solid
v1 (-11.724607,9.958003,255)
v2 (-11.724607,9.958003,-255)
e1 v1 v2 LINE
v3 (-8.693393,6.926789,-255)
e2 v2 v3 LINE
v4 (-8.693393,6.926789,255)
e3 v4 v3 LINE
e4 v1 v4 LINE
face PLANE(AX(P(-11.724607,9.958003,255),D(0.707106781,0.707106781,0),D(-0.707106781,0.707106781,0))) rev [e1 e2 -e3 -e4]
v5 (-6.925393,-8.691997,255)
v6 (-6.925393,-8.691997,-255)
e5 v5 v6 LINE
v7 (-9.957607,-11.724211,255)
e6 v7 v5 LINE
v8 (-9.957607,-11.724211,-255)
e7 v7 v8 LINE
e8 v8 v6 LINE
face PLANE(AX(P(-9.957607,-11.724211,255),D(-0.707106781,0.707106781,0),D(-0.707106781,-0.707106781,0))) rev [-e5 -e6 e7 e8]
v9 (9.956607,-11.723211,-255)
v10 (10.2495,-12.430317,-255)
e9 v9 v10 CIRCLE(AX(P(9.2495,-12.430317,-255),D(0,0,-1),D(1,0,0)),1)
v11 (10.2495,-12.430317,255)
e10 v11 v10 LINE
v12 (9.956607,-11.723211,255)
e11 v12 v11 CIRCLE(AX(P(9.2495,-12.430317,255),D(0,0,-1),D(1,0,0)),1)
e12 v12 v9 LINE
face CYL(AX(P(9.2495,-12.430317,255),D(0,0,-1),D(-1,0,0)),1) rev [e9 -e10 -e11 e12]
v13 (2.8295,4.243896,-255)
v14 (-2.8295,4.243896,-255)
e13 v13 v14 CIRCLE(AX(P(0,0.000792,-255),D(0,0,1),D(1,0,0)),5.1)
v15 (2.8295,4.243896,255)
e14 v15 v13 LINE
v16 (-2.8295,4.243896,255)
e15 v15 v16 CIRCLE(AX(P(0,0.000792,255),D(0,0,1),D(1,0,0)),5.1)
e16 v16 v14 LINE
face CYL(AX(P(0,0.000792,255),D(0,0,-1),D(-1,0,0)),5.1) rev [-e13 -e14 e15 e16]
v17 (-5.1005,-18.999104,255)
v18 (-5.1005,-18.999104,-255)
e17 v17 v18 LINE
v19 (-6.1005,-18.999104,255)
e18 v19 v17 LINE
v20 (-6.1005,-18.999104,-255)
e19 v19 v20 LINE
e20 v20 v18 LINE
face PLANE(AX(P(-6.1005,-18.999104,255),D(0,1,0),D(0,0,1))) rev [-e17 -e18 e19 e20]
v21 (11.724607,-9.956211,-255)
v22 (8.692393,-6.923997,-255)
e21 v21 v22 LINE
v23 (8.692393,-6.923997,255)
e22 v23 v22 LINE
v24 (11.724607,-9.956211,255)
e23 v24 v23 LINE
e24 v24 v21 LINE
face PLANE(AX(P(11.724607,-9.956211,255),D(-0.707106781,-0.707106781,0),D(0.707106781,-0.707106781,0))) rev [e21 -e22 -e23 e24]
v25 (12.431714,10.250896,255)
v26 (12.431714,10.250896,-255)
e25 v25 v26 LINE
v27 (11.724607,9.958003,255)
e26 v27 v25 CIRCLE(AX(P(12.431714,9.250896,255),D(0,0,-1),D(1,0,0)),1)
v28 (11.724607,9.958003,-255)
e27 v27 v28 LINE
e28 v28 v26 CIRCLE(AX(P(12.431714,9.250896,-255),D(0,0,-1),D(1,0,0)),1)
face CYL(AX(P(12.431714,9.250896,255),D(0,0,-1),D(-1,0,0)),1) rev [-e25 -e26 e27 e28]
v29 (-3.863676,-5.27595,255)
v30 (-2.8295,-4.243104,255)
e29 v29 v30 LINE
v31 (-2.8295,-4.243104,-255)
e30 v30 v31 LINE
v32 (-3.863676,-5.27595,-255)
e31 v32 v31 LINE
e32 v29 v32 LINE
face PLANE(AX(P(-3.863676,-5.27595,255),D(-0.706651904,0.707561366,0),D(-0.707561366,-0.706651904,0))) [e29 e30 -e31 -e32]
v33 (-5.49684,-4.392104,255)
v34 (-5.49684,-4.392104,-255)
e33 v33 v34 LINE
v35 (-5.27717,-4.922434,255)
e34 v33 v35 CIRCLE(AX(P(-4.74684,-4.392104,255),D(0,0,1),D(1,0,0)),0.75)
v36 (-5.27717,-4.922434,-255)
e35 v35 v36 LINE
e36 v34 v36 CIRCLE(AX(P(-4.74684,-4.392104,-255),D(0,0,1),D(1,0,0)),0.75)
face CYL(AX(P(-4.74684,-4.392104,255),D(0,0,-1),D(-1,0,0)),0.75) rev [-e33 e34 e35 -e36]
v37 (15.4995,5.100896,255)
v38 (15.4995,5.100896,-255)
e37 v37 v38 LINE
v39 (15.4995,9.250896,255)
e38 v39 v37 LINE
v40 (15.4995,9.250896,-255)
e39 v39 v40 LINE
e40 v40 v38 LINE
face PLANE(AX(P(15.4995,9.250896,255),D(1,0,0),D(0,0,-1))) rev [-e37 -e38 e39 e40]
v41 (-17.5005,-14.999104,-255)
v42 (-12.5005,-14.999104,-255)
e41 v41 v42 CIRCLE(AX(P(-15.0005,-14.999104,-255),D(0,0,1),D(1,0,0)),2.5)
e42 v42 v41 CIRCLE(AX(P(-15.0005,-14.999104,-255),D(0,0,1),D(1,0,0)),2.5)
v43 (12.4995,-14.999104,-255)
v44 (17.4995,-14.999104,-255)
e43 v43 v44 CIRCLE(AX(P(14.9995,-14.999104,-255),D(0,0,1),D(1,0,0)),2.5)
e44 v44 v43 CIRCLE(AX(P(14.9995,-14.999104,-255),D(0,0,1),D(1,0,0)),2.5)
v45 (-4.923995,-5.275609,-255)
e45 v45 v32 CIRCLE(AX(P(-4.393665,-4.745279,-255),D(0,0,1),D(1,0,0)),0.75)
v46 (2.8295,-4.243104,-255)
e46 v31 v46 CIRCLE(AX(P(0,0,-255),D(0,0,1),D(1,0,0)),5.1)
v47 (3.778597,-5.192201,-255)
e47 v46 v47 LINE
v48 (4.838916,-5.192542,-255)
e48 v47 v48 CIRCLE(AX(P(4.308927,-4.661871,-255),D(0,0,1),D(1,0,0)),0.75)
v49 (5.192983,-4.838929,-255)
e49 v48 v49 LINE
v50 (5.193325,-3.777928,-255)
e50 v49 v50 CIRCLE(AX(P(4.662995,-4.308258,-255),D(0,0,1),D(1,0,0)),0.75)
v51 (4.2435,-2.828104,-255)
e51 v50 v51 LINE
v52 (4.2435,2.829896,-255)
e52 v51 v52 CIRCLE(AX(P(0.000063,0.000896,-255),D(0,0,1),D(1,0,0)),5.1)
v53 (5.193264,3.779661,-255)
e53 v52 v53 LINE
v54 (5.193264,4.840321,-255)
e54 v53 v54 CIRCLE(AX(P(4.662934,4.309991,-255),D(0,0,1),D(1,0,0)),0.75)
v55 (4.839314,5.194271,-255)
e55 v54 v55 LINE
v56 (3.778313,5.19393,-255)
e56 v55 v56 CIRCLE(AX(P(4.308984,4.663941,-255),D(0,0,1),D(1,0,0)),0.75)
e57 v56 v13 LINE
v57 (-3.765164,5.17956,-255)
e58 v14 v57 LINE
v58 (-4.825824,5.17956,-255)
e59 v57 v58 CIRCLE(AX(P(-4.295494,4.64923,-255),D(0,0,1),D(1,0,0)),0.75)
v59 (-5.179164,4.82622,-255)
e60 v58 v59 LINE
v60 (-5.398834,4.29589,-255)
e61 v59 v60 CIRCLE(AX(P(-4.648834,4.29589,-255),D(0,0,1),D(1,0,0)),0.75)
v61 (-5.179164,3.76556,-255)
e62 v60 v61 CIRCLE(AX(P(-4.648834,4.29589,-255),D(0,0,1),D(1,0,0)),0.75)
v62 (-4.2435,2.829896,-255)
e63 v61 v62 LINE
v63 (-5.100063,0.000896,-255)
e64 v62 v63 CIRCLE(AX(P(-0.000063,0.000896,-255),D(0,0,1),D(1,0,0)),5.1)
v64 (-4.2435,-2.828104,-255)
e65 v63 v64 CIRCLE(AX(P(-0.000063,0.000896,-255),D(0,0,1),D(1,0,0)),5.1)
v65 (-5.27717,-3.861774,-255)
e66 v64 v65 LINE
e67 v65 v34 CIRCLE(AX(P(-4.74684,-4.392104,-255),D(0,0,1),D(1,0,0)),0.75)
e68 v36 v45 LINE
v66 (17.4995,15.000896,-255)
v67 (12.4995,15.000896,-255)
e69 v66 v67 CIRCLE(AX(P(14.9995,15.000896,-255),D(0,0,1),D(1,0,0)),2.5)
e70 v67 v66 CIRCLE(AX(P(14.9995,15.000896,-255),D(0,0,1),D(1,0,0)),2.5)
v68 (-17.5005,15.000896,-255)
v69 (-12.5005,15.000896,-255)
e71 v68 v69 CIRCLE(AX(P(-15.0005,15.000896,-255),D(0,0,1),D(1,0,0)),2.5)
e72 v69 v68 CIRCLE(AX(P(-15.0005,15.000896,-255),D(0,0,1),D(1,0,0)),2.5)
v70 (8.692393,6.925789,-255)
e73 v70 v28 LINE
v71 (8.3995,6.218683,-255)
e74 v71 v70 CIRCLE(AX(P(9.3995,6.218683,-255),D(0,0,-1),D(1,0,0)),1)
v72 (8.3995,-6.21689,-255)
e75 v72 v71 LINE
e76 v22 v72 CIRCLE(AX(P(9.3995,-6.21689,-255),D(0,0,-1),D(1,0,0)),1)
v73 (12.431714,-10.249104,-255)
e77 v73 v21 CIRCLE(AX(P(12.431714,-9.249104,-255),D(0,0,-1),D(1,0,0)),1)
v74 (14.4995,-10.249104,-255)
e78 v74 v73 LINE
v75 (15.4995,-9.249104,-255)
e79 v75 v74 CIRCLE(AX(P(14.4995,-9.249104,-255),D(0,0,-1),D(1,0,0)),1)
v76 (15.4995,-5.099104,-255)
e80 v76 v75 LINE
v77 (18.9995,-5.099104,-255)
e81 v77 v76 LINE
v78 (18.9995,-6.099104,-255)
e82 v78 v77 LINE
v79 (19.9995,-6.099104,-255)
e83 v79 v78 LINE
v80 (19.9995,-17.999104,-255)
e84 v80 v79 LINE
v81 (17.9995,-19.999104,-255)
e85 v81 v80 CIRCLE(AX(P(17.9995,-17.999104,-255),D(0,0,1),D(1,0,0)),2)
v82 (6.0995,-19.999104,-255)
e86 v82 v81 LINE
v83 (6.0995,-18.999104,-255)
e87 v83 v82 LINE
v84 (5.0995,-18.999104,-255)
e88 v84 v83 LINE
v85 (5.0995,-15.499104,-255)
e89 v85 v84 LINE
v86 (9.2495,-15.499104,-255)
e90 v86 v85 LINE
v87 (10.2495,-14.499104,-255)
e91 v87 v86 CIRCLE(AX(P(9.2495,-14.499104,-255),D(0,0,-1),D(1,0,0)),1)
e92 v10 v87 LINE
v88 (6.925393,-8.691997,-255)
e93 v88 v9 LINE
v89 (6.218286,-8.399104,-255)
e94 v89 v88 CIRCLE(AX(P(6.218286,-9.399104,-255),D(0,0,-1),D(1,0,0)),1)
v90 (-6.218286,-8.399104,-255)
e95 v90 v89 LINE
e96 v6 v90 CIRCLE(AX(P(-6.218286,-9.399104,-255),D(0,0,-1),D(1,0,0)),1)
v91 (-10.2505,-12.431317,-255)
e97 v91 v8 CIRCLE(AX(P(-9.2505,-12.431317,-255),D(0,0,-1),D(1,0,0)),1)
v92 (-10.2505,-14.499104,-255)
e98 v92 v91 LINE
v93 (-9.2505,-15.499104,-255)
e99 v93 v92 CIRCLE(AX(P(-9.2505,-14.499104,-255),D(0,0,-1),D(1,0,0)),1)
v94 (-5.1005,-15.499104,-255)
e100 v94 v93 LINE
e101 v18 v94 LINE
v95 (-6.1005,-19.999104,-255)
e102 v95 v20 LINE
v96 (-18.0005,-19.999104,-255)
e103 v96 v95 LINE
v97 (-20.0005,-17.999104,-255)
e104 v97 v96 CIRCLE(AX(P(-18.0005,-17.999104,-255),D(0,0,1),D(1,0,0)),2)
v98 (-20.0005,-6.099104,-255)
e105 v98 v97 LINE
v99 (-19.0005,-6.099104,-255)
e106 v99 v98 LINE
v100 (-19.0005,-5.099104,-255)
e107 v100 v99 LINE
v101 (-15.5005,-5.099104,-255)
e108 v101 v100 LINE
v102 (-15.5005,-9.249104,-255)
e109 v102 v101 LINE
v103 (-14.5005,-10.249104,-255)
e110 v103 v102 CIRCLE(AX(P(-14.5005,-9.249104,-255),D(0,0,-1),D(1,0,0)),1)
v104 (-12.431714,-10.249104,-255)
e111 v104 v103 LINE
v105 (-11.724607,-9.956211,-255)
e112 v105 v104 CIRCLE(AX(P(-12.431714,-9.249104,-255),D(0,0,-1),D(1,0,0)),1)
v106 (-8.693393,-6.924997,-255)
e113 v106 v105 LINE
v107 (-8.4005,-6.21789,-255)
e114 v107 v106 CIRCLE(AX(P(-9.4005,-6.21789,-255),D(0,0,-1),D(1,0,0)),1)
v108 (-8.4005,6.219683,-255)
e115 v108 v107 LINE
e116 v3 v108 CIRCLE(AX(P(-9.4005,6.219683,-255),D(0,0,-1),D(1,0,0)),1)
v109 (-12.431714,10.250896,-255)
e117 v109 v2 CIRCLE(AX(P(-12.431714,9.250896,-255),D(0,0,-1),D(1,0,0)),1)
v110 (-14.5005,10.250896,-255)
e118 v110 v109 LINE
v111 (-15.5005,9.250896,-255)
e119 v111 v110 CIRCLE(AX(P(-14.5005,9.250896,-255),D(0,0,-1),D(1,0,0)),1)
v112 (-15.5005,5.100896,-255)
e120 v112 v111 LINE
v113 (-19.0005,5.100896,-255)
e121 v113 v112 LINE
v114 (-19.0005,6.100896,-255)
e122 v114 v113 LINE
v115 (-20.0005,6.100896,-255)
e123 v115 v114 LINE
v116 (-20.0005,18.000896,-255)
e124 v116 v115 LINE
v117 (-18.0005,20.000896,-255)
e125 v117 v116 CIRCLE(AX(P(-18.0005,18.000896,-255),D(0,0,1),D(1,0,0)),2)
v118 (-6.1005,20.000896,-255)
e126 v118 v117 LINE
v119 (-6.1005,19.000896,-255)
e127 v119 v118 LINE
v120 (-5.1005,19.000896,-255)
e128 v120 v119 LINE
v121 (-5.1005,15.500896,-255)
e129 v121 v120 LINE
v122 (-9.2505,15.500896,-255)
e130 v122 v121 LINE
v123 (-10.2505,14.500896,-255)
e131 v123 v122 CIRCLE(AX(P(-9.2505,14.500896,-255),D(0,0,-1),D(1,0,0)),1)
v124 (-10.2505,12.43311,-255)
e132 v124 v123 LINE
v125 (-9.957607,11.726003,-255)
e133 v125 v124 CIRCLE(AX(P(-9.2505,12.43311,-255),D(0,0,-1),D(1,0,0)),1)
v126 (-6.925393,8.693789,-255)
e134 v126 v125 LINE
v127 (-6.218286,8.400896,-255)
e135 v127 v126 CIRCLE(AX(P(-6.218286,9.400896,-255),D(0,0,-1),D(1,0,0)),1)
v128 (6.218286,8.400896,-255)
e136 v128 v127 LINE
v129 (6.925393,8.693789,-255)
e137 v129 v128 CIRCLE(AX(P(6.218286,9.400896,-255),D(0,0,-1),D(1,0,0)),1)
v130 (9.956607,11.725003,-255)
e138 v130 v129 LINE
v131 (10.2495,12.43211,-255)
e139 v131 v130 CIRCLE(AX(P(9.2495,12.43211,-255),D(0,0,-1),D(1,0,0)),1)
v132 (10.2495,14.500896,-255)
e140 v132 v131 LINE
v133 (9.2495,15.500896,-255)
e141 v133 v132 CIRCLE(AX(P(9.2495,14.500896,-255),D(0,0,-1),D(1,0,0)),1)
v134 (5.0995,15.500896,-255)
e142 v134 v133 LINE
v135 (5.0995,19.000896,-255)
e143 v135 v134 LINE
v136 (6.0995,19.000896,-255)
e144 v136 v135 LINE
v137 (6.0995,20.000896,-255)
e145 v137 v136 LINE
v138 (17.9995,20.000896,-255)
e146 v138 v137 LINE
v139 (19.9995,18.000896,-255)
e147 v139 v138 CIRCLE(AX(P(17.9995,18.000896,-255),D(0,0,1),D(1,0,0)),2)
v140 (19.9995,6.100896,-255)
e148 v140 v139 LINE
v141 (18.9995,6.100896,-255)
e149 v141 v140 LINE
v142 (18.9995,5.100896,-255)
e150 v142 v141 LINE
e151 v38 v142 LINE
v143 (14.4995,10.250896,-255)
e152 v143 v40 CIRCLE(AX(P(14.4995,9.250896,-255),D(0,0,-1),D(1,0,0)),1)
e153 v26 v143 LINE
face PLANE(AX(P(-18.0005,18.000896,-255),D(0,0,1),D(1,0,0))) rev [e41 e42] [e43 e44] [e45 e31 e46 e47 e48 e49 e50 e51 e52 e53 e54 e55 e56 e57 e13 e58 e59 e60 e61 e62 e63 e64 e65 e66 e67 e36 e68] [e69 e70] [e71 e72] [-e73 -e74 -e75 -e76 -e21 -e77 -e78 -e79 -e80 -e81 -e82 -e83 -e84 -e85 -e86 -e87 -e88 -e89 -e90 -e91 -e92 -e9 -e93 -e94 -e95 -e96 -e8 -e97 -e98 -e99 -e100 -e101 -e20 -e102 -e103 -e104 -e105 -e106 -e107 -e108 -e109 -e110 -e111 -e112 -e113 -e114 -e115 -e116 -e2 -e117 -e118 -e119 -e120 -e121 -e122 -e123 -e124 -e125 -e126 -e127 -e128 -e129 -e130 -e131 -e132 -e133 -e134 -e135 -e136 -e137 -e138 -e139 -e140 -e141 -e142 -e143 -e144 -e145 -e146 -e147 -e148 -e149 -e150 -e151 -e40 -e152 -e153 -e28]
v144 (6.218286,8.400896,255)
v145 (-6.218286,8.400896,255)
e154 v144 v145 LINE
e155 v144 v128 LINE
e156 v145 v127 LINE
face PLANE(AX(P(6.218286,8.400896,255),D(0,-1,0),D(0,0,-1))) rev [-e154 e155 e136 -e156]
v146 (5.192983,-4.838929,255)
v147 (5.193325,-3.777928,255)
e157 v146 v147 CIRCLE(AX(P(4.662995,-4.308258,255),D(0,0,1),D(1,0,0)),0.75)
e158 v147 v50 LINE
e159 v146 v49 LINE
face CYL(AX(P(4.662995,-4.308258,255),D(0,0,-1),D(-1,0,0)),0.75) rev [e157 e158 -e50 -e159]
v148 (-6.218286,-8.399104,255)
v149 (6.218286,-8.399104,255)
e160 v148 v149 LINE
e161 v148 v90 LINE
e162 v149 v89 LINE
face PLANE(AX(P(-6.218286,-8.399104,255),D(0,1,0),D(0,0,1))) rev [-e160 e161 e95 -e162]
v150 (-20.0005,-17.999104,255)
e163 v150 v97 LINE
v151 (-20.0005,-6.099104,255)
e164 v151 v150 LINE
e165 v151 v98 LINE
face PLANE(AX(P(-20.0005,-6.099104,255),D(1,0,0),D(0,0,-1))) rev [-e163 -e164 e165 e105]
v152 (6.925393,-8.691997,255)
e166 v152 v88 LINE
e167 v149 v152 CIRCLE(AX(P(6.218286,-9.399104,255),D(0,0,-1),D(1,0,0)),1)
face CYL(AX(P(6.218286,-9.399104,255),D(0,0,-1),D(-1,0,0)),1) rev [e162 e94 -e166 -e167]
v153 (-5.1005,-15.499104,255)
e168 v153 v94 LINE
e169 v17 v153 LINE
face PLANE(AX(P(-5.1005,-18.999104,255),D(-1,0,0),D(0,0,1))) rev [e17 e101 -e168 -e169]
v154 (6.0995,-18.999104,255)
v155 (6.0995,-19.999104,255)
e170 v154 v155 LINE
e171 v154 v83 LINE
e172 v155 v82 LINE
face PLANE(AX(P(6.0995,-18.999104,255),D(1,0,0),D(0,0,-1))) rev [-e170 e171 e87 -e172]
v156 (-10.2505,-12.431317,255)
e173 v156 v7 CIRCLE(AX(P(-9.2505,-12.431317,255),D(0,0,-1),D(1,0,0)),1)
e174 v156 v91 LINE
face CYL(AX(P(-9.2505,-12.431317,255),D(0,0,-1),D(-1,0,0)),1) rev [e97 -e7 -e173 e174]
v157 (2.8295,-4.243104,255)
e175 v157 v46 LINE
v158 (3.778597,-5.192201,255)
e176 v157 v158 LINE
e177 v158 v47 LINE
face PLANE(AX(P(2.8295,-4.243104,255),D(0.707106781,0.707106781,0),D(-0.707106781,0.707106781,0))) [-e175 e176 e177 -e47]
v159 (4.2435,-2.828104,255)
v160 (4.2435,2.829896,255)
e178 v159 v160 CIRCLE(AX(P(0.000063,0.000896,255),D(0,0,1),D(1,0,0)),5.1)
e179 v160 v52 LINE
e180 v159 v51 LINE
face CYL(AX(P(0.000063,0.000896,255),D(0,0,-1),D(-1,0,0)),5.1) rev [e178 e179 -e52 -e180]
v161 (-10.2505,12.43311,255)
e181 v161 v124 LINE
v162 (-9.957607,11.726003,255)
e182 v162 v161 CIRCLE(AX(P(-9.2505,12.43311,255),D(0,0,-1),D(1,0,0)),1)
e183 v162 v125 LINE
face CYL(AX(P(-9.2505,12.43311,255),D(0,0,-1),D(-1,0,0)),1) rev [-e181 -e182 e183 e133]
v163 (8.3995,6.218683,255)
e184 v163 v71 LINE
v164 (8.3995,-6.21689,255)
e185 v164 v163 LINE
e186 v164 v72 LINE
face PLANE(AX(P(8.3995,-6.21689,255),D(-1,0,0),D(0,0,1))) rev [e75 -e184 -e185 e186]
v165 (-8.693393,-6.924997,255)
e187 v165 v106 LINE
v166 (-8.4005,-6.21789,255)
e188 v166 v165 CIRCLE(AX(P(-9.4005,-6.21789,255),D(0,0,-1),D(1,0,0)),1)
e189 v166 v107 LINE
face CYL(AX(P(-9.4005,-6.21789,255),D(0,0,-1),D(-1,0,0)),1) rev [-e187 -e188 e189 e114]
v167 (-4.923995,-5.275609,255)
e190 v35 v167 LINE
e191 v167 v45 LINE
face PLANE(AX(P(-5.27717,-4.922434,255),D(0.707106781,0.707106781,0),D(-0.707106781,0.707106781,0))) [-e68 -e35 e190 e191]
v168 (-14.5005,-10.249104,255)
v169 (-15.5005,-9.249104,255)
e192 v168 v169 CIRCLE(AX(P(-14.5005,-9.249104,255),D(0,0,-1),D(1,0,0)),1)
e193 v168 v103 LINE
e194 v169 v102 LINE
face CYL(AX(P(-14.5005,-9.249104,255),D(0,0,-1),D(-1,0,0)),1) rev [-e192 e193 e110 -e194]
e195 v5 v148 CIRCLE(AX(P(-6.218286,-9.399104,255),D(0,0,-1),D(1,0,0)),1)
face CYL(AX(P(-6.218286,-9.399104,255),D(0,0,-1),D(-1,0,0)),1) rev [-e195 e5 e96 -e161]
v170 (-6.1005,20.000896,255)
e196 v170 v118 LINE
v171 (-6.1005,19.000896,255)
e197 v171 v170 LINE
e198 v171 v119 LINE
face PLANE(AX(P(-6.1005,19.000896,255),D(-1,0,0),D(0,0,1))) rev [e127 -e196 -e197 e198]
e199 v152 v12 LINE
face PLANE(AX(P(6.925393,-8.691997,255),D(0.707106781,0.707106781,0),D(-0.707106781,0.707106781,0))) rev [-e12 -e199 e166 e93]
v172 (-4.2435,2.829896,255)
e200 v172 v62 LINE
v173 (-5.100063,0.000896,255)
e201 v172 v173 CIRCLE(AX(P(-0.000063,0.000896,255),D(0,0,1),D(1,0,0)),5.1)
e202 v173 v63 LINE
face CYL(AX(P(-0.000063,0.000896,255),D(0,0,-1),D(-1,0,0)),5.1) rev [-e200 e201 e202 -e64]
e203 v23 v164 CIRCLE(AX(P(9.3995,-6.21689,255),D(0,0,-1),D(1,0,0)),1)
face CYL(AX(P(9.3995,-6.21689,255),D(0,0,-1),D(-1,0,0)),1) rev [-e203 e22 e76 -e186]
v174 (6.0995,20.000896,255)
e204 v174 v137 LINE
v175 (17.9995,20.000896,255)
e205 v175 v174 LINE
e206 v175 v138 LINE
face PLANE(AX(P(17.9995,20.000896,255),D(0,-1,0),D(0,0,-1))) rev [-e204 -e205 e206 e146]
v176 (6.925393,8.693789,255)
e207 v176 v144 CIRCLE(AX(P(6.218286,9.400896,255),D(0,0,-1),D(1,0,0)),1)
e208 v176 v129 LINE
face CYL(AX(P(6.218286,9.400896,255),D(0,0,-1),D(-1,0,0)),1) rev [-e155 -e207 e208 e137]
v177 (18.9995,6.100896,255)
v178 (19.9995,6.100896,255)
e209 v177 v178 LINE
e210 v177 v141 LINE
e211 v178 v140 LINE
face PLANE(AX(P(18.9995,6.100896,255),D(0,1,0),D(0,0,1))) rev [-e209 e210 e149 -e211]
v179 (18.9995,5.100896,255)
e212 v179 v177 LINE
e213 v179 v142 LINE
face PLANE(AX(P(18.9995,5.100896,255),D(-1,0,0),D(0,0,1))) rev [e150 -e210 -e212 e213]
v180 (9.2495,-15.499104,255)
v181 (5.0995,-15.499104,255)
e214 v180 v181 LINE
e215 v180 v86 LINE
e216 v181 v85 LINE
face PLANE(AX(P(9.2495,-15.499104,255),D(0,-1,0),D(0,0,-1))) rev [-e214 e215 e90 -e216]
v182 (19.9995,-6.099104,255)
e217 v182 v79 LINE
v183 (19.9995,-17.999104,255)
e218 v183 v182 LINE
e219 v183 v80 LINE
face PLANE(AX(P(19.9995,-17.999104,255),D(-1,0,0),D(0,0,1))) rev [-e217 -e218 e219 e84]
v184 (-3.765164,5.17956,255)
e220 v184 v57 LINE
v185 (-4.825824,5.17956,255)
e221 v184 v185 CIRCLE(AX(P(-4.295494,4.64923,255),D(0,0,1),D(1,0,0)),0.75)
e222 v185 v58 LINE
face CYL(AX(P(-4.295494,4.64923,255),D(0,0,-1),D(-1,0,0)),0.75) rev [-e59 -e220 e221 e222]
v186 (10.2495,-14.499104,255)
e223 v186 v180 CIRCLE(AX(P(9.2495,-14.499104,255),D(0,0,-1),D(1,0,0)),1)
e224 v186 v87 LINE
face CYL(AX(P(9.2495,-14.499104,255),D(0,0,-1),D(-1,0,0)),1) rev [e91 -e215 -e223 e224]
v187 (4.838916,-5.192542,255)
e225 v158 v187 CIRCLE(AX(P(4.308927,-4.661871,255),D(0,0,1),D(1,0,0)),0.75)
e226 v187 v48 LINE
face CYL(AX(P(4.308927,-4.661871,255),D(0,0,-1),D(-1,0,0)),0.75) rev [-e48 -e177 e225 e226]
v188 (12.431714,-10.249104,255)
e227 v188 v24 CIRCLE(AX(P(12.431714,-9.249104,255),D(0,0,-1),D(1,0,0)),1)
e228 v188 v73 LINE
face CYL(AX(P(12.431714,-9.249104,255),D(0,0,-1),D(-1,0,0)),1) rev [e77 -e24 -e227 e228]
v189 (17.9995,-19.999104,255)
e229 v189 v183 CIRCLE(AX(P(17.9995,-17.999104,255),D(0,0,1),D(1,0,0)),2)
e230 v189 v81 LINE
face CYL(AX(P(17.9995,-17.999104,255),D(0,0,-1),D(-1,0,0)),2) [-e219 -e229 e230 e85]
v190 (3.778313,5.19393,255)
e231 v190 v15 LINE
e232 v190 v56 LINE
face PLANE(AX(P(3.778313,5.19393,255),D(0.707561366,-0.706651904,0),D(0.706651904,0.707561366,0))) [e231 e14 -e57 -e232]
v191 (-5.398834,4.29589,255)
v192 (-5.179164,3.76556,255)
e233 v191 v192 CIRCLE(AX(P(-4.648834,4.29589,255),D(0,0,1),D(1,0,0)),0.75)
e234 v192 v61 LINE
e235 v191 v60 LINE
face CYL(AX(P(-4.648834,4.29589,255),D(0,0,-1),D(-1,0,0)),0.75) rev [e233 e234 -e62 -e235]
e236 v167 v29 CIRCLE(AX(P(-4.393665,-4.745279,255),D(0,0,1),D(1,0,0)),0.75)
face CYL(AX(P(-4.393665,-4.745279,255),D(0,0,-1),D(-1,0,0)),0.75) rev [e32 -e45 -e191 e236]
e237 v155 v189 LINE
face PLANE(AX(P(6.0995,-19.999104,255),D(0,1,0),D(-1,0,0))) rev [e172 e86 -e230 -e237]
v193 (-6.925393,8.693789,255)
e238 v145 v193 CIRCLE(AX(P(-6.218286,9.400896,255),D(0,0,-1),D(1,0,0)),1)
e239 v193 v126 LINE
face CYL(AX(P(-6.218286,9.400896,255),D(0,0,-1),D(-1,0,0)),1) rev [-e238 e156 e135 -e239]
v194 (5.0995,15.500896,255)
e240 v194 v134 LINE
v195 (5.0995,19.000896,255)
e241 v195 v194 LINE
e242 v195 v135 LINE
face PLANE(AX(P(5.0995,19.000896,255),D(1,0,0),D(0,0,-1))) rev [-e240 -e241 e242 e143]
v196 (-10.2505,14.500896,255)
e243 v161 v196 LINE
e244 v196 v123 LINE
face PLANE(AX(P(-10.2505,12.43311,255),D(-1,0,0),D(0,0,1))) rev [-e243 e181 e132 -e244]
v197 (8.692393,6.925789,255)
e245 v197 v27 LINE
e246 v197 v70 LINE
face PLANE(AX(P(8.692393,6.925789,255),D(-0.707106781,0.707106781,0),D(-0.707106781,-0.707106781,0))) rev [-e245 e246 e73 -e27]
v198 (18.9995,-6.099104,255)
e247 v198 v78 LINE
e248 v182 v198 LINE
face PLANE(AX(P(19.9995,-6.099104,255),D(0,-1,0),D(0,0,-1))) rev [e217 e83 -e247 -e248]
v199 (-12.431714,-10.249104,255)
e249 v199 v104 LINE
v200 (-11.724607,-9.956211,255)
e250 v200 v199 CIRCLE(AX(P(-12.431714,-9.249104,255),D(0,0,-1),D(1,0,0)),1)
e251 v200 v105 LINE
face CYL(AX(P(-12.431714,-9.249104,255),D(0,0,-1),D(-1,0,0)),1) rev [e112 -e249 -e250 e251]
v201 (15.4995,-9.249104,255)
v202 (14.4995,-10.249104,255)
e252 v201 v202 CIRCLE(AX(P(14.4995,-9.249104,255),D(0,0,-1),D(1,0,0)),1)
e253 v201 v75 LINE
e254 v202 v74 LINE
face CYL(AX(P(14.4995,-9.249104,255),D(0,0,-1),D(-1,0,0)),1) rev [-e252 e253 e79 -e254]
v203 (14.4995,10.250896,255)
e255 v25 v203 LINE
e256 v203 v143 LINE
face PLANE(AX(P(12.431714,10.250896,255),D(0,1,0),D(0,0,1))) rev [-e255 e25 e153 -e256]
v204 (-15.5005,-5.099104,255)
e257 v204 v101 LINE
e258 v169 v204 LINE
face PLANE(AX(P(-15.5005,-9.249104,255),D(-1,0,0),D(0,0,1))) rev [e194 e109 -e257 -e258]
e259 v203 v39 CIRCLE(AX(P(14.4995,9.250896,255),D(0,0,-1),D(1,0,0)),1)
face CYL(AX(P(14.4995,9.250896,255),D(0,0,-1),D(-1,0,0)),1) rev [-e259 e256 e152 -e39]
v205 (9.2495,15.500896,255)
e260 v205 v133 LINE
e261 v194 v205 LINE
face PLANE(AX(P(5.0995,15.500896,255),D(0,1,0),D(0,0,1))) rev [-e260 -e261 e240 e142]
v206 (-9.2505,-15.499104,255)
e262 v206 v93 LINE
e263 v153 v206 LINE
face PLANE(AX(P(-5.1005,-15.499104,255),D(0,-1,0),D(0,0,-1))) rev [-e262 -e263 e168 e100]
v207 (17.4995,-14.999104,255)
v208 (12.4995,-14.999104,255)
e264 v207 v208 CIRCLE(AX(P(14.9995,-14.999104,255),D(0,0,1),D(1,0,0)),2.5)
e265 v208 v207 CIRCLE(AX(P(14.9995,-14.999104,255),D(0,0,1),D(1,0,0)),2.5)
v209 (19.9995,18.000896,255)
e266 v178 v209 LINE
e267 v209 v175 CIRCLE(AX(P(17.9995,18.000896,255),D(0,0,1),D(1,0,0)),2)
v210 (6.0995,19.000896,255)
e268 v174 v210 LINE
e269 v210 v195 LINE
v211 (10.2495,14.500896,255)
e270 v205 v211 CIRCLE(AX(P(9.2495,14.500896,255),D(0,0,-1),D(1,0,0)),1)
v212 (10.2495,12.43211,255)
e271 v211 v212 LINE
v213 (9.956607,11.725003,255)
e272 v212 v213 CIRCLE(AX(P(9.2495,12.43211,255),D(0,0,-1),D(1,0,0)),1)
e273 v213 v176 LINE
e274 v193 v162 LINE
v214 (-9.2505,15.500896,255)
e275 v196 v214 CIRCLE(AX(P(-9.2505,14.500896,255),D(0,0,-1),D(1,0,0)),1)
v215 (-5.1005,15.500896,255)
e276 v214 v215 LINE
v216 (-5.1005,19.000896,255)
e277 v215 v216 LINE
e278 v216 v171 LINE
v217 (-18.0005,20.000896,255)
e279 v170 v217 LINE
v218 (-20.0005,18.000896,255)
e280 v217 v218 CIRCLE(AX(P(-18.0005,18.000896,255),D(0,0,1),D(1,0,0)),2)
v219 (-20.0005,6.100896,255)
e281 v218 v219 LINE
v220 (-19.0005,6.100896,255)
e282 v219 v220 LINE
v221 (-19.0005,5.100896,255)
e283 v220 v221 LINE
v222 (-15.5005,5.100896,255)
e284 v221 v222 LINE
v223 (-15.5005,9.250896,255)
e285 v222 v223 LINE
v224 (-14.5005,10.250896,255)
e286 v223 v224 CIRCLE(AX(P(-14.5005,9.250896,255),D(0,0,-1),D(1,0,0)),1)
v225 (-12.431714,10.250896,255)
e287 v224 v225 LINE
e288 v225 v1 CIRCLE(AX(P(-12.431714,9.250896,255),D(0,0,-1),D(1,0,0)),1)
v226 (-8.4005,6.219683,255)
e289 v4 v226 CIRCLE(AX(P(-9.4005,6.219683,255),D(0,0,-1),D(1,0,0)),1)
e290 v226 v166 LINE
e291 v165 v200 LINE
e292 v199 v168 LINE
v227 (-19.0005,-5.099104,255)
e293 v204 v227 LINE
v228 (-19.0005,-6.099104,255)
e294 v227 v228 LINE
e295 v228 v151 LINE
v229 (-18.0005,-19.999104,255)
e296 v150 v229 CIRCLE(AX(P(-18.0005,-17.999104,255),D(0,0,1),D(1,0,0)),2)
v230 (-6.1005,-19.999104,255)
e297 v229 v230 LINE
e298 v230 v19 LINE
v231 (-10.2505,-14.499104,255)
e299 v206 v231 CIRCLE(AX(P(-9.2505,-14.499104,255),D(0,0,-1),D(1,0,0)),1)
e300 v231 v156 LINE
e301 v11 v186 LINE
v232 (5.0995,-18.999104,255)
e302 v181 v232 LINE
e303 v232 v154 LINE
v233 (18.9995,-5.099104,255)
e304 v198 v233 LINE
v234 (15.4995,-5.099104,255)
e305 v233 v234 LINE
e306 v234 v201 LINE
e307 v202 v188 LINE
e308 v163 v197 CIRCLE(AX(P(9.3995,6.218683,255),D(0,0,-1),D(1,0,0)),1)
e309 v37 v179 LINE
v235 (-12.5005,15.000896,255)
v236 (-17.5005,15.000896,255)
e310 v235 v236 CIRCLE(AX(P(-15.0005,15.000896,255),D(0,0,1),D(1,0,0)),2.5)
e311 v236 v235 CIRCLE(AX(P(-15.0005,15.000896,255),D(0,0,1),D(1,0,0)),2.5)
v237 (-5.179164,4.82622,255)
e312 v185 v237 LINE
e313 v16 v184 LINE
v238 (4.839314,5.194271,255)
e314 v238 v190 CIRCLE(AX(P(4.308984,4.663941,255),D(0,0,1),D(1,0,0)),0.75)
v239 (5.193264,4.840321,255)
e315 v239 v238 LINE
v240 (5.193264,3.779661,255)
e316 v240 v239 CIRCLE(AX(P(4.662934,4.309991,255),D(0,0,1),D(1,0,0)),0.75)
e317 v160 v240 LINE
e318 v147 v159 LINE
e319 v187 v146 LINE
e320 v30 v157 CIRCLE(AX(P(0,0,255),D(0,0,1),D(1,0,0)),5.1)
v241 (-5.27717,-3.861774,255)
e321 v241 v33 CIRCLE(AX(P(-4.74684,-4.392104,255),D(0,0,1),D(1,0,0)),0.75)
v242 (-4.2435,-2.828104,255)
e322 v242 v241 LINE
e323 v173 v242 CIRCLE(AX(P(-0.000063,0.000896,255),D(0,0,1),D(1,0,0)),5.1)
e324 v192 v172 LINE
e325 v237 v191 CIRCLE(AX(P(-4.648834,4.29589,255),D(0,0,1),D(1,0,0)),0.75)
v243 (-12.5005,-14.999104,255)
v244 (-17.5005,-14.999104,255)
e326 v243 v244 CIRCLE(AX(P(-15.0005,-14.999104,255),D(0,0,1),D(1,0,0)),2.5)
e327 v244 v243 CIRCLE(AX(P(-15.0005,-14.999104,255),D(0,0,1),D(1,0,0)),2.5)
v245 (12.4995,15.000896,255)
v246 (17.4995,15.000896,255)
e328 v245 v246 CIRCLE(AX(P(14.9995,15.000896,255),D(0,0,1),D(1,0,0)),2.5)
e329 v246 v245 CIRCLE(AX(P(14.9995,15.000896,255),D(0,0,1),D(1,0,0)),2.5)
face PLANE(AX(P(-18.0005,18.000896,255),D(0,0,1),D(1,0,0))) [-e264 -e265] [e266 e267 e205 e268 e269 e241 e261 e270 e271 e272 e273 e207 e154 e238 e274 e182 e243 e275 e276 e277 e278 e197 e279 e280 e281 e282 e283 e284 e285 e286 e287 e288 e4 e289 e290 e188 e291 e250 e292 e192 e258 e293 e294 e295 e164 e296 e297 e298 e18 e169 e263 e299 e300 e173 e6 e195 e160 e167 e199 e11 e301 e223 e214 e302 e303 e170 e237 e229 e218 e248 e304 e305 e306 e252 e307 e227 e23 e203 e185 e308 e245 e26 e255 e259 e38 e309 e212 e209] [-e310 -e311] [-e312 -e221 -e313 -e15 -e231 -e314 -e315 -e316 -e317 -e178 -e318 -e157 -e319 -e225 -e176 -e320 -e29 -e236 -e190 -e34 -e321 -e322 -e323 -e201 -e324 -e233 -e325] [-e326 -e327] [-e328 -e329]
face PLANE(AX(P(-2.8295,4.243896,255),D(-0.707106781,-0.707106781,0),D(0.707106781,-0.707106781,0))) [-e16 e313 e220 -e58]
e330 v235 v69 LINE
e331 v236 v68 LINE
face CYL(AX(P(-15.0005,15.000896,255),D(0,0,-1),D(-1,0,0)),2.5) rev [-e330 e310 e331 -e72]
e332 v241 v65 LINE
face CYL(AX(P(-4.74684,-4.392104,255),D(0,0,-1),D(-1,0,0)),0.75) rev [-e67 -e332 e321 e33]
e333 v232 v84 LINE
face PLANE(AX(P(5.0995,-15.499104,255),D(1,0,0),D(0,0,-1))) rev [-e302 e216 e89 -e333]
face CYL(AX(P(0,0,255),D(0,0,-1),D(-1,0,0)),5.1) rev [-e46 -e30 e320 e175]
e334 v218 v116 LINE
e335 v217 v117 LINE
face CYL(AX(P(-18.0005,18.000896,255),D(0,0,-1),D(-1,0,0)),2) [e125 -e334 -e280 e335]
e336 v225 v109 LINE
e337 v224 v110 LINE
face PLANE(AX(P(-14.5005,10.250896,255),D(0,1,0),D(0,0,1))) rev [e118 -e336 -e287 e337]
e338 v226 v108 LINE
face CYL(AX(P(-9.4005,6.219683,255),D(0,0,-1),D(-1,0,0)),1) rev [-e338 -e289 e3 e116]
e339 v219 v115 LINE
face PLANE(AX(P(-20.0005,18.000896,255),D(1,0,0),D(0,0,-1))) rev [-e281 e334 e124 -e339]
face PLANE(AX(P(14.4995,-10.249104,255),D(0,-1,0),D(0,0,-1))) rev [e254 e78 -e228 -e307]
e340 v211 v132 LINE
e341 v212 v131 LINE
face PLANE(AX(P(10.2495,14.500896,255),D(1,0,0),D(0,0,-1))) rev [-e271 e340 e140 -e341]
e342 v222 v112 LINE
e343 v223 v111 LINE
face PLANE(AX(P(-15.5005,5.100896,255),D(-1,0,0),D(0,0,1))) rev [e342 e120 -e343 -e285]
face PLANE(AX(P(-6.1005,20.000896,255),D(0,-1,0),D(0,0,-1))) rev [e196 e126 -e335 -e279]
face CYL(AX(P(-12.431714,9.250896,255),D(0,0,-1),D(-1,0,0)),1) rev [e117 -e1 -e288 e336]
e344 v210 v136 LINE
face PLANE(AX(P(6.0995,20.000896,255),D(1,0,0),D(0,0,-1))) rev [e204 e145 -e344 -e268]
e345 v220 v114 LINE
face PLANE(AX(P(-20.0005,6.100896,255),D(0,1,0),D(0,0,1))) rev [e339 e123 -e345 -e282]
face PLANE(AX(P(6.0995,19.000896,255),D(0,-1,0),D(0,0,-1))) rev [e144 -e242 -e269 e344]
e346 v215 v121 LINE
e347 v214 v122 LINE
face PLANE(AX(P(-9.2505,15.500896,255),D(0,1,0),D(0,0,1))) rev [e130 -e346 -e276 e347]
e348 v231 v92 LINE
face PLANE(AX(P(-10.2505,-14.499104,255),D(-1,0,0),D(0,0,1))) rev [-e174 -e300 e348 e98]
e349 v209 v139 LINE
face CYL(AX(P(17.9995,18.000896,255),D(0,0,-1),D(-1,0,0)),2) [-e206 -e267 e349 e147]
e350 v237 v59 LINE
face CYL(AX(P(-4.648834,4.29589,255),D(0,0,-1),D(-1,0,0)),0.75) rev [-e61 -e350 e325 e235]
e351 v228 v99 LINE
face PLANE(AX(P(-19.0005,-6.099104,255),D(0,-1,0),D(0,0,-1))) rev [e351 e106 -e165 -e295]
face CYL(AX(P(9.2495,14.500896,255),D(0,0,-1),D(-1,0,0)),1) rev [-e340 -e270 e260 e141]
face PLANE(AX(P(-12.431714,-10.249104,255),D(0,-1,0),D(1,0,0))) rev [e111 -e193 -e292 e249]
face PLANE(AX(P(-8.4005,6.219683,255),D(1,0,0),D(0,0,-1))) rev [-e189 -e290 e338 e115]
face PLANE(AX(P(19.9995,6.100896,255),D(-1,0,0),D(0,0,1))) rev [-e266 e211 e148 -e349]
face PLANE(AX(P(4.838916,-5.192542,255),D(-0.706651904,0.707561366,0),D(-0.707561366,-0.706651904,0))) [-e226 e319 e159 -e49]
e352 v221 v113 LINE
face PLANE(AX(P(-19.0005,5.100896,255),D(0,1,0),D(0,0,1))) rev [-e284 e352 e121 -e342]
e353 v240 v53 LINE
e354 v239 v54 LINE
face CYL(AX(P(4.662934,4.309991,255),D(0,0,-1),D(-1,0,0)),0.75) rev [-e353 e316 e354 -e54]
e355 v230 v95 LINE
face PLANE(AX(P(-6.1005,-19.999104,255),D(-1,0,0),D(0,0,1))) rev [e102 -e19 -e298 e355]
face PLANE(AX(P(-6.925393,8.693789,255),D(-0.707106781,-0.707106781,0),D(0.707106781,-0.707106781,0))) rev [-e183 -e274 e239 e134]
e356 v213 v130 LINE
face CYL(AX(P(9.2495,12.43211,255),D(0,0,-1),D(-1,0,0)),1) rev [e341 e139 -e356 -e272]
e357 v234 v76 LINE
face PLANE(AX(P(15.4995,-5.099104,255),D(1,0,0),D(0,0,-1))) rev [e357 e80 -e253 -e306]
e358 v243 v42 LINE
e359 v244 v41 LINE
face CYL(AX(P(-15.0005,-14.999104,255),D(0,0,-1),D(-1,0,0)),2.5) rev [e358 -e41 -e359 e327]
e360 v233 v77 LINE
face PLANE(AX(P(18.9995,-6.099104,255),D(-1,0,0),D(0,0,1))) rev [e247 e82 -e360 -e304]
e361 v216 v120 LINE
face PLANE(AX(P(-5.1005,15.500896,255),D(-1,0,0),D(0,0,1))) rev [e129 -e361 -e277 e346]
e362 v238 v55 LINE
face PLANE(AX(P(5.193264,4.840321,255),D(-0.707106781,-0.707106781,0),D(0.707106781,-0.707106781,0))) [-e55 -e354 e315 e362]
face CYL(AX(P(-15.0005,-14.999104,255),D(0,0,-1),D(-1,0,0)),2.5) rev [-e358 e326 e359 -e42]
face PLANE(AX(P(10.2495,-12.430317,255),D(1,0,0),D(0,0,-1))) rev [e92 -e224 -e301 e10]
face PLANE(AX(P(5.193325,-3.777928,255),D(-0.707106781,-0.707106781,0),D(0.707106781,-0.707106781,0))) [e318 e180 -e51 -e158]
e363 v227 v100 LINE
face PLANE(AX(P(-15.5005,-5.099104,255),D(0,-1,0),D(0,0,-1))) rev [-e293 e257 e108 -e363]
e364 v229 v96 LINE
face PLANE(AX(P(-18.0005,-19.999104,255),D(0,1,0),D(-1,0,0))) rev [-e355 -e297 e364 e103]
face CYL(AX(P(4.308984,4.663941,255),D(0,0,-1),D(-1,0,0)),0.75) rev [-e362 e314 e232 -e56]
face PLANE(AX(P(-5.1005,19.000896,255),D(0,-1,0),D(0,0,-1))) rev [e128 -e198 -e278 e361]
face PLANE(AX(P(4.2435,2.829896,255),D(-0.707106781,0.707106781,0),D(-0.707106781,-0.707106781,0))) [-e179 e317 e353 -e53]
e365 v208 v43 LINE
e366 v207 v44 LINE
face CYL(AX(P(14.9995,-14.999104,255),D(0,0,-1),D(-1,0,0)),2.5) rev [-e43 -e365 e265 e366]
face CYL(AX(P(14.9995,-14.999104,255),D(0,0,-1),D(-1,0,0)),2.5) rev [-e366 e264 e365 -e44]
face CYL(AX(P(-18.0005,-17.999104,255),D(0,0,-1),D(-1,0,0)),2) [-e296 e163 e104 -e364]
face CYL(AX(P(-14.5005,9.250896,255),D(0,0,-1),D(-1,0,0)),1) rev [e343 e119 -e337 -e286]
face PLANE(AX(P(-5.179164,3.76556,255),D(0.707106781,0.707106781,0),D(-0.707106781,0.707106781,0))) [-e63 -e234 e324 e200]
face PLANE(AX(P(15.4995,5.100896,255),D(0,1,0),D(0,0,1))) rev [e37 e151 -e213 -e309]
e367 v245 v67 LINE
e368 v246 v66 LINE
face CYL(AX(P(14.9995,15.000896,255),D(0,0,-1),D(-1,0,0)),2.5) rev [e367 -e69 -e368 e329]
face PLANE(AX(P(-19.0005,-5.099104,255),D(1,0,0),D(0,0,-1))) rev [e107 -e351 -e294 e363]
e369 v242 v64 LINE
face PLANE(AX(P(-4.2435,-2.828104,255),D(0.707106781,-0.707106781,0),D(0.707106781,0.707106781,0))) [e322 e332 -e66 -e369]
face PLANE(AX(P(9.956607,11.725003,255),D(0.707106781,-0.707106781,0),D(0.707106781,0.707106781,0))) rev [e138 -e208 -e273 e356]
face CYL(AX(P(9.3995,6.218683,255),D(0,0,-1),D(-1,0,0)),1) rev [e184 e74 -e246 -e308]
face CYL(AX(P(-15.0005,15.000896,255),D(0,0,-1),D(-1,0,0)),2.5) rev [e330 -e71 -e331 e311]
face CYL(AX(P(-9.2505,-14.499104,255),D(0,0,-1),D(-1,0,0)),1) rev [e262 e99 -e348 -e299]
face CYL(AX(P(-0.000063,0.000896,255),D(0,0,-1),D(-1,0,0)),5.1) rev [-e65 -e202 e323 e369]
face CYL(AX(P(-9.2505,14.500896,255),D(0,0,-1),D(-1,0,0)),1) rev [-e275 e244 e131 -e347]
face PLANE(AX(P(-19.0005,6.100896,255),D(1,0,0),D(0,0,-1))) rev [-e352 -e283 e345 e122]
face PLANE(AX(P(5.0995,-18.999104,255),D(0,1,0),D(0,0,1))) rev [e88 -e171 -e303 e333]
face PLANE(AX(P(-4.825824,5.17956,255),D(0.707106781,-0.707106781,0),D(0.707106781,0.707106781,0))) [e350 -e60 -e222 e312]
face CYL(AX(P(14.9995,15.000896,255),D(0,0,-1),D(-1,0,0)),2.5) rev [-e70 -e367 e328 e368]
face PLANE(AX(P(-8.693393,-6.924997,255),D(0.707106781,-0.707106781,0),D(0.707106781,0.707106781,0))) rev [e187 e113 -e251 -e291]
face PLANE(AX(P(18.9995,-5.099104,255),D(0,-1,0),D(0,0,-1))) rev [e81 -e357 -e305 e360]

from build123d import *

# Parameters (mm, degrees)
SKETCH1_R           = 2.5
BOSS_EXTRUDE1_DEPTH = 255


with BuildPart() as part:
    # Sketch1 → Boss-Extrude1 (new, symmetric)
    with BuildSketch(Plane.XY):
        with BuildLine():
            Line((-5.1005, 15.500896213), (-5.1005, 19.000896213))
            Line((-5.1005, 19.000896213), (-6.1005, 19.000896213))
            Line((-6.1005, 19.000896213), (-6.1005, 20.000896213))
            Line((-6.1005, 20.000896213), (-18.0005, 20.000896213))
            ThreePointArc((-18.0005, 20.000896213), (-19.414713562, 19.415109775), (-20.0005, 18.000896213))
            Line((-20.0005, 18.000896213), (-20.0005, 6.100896213))
            Line((-20.0005, 6.100896213), (-19.0005, 6.100896213))
            Line((-19.0005, 6.100896213), (-19.0005, 5.100896213))
            Line((-19.0005, 5.100896213), (-15.5005, 5.100896213))
            Line((-15.5005, 5.100896213), (-15.5005, 9.250896213))
            ThreePointArc((-15.5005, 9.250896213), (-15.207606781, 9.958002994), (-14.5005, 10.250896213))
            Line((-14.5005, 10.250896213), (-12.431713562, 10.250896213))
            ThreePointArc((-12.431713562, 10.250896213), (-12.049030228, 10.174775786), (-11.724606932, 9.958003144))
            Line((-11.724606932, 9.958003144), (-8.693393219, 6.926789431))
            ThreePointArc((-8.693393219, 6.926789431), (-8.476620546, 6.602366272), (-8.4005, 6.21968306))
            Line((-8.4005, 6.21968306), (-8.4005, -6.217890225))
            ThreePointArc((-8.4005, -6.217890225), (-8.476620502, -6.60057374), (-8.693393346, -6.924997133))
            Line((-8.693393346, -6.924997133), (-11.724606781, -9.956210569))
            ThreePointArc((-11.724606781, -9.956210569), (-12.049030198, -10.172983348), (-12.431713709, -10.249103787))
            Line((-12.431713709, -10.249103787), (-14.5005, -10.249103787))
            ThreePointArc((-14.5005, -10.249103787), (-15.207606781, -9.956210569), (-15.5005, -9.249103787))
            Line((-15.5005, -9.249103787), (-15.5005, -5.099103787))
            Line((-15.5005, -5.099103787), (-19.0005, -5.099103787))
            Line((-19.0005, -5.099103787), (-19.0005, -6.099103787))
            Line((-19.0005, -6.099103787), (-20.0005, -6.099103787))
            Line((-20.0005, -6.099103787), (-20.0005, -17.999103787))
            ThreePointArc((-20.0005, -17.999103787), (-19.414713562, -19.41331735), (-18.0005, -19.999103787))
            Line((-18.0005, -19.999103787), (-6.1005, -19.999103787))
            Line((-6.1005, -19.999103787), (-6.1005, -18.999103787))
            Line((-6.1005, -18.999103787), (-5.1005, -18.999103787))
            Line((-5.1005, -18.999103787), (-5.1005, -15.499103787))
            Line((-5.1005, -15.499103787), (-9.2505, -15.499103787))
            ThreePointArc((-9.2505, -15.499103787), (-9.957606781, -15.206210569), (-10.2505, -14.499103787))
            Line((-10.2505, -14.499103787), (-10.2505, -12.43131735))
            ThreePointArc((-10.2505, -12.43131735), (-10.174379535, -12.048633922), (-9.957606789, -11.724210576))
            Line((-9.957606789, -11.724210576), (-6.925393219, -8.691997006))
            ThreePointArc((-6.925393219, -8.691997006), (-6.60096987, -8.475224255), (-6.218286438, -8.399103787))
            Line((-6.218286438, -8.399103787), (6.218286438, -8.399103787))
            ThreePointArc((6.218286438, -8.399103787), (6.600969772, -8.475224214), (6.925393068, -8.691996856))
            Line((6.925393068, -8.691996856), (9.956606781, -11.723210569))
            ThreePointArc((9.956606781, -11.723210569), (10.173379454, -12.047633728), (10.2495, -12.43031694))
            Line((10.2495, -12.43031694), (10.2495, -14.499103787))
            ThreePointArc((10.2495, -14.499103787), (9.956606781, -15.206210569), (9.2495, -15.499103787))
            Line((9.2495, -15.499103787), (5.0995, -15.499103787))
            Line((5.0995, -15.499103787), (5.0995, -18.999103787))
            Line((5.0995, -18.999103787), (6.0995, -18.999103787))
            Line((6.0995, -18.999103787), (6.0995, -19.999103787))
            Line((6.0995, -19.999103787), (17.9995, -19.999103787))
            ThreePointArc((17.9995, -19.999103787), (19.413713562, -19.41331735), (19.9995, -17.999103787))
            Line((19.9995, -17.999103787), (19.9995, -6.099103787))
            Line((19.9995, -6.099103787), (18.9995, -6.099103787))
            Line((18.9995, -6.099103787), (18.9995, -5.099103787))
            Line((18.9995, -5.099103787), (15.4995, -5.099103787))
            Line((15.4995, -5.099103787), (15.4995, -9.249103787))
            ThreePointArc((15.4995, -9.249103787), (15.206606781, -9.956210569), (14.4995, -10.249103787))
            Line((14.4995, -10.249103787), (12.431713562, -10.249103787))
            ThreePointArc((12.431713562, -10.249103787), (12.049030135, -10.172983322), (11.724606789, -9.956210576))
            Line((11.724606789, -9.956210576), (8.692393219, -6.923997006))
            ThreePointArc((8.692393219, -6.923997006), (8.475620467, -6.599573657), (8.3995, -6.216890225))
            Line((8.3995, -6.216890225), (8.3995, 6.21868265))
            ThreePointArc((8.3995, 6.21868265), (8.475620465, 6.601366078), (8.692393211, 6.925789424))
            Line((8.692393211, 6.925789424), (11.724606781, 9.958002994))
            ThreePointArc((11.724606781, 9.958002994), (12.04903013, 10.174775745), (12.431713562, 10.250896213))
            Line((12.431713562, 10.250896213), (14.4995, 10.250896213))
            ThreePointArc((14.4995, 10.250896213), (15.206606781, 9.958002994), (15.4995, 9.250896213))
            Line((15.4995, 9.250896213), (15.4995, 5.100896213))
            Line((15.4995, 5.100896213), (18.9995, 5.100896213))
            Line((18.9995, 5.100896213), (18.9995, 6.100896213))
            Line((18.9995, 6.100896213), (19.9995, 6.100896213))
            Line((19.9995, 6.100896213), (19.9995, 18.000896213))
            ThreePointArc((19.9995, 18.000896213), (19.413713562, 19.415109775), (17.9995, 20.000896213))
            Line((17.9995, 20.000896213), (6.0995, 20.000896213))
            Line((6.0995, 20.000896213), (6.0995, 19.000896213))
            Line((6.0995, 19.000896213), (5.0995, 19.000896213))
            Line((5.0995, 19.000896213), (5.0995, 15.500896213))
            Line((5.0995, 15.500896213), (9.2495, 15.500896213))
            ThreePointArc((9.2495, 15.500896213), (9.956606781, 15.208002994), (10.2495, 14.500896213))
            Line((10.2495, 14.500896213), (10.2495, 12.432109775))
            ThreePointArc((10.2495, 12.432109775), (10.173379498, 12.04942626), (9.956606654, 11.725002867))
            Line((9.956606654, 11.725002867), (6.925393219, 8.693789431))
            ThreePointArc((6.925393219, 8.693789431), (6.600969802, 8.477016652), (6.218286291, 8.400896213))
            Line((6.218286291, 8.400896213), (-6.218286438, 8.400896213))
            ThreePointArc((-6.218286438, 8.400896213), (-6.600969865, 8.477016678), (-6.925393211, 8.693789424))
            Line((-6.925393211, 8.693789424), (-9.957606781, 11.726002994))
            ThreePointArc((-9.957606781, 11.726002994), (-10.174379533, 12.050426343), (-10.2505, 12.433109775))
            Line((-10.2505, 12.433109775), (-10.2505, 14.500896213))
            ThreePointArc((-10.2505, 14.500896213), (-9.957606781, 15.208002994), (-9.2505, 15.500896213))
            Line((-9.2505, 15.500896213), (-5.1005, 15.500896213))
        make_face()
        with Locations((-15.0005, 15.000896213)):
            Circle(SKETCH1_R, mode=Mode.SUBTRACT)
        with Locations((14.9995, -14.999103787)):
            Circle(SKETCH1_R, mode=Mode.SUBTRACT)
        with Locations((-15.0005, -14.999103787)):
            Circle(SKETCH1_R, mode=Mode.SUBTRACT)
        with Locations((14.9995, 15.000896213)):
            Circle(SKETCH1_R, mode=Mode.SUBTRACT)
        with BuildLine():
            Line((-5.179163629, 3.765559841), (-4.2435, 2.829896213))
            ThreePointArc((-4.2435, 2.829896213), (-5.100062832, 0.000896213), (-4.2435, -2.828103787))
            Line((-4.2435, -2.828103787), (-5.277169914, -3.861773701))
            ThreePointArc((-5.277169914, -3.861773701), (-5.496839828, -4.392103787), (-5.277169914, -4.922433873))
            Line((-5.277169914, -4.922433873), (-4.923994614, -5.275609174))
            ThreePointArc((-4.923994614, -5.275609174), (-4.393905685, -5.495279049), (-3.8636756, -5.275950112))
            Line((-3.8636756, -5.275950112), (-2.8295, -4.243103787))
            ThreePointArc((-2.8295, -4.243103787), (0, -5.1), (2.8295, -4.243103787))
            Line((2.8295, -4.243103787), (3.778597046, -5.192200834))
            ThreePointArc((3.778597046, -5.192200834), (4.308685975, -5.411870709), (4.83891606, -5.192541772))
            Line((4.83891606, -5.192541772), (5.192983438, -4.838929494))
            ThreePointArc((5.192983438, -4.838929494), (5.412994471, -4.308499627), (5.193324596, -3.777928383))
            Line((5.193324596, -3.777928383), (4.2435, -2.828103787))
            ThreePointArc((4.2435, -2.828103787), (5.100062832, 0.000896213), (4.2435, 2.829896213))
            Line((4.2435, 2.829896213), (5.193264407, 3.77966062))
            ThreePointArc((5.193264407, 3.77966062), (5.412934321, 4.309990706), (5.193264407, 4.840320791))
            Line((5.193264407, 4.840320791), (4.839313907, 5.194271291))
            ThreePointArc((4.839313907, 5.194271291), (4.308742664, 5.413941166), (3.778312797, 5.193930133))
            Line((3.778312797, 5.193930133), (2.8295, 4.243896213))
            ThreePointArc((2.8295, 4.243896213), (0, 5.100792425), (-2.8295, 4.243896213))
            Line((-2.8295, 4.243896213), (-3.765163629, 5.179559841))
            ThreePointArc((-3.765163629, 5.179559841), (-4.295493715, 5.399229756), (-4.825823801, 5.179559841))
            Line((-4.825823801, 5.179559841), (-5.179163629, 4.826220013))
            ThreePointArc((-5.179163629, 4.826220013), (-5.398833543, 4.295889927), (-5.179163629, 3.765559841))
        make_face(mode=Mode.SUBTRACT)
    extrude(amount=BOSS_EXTRUDE1_DEPTH, both=True)


solid = part.part
